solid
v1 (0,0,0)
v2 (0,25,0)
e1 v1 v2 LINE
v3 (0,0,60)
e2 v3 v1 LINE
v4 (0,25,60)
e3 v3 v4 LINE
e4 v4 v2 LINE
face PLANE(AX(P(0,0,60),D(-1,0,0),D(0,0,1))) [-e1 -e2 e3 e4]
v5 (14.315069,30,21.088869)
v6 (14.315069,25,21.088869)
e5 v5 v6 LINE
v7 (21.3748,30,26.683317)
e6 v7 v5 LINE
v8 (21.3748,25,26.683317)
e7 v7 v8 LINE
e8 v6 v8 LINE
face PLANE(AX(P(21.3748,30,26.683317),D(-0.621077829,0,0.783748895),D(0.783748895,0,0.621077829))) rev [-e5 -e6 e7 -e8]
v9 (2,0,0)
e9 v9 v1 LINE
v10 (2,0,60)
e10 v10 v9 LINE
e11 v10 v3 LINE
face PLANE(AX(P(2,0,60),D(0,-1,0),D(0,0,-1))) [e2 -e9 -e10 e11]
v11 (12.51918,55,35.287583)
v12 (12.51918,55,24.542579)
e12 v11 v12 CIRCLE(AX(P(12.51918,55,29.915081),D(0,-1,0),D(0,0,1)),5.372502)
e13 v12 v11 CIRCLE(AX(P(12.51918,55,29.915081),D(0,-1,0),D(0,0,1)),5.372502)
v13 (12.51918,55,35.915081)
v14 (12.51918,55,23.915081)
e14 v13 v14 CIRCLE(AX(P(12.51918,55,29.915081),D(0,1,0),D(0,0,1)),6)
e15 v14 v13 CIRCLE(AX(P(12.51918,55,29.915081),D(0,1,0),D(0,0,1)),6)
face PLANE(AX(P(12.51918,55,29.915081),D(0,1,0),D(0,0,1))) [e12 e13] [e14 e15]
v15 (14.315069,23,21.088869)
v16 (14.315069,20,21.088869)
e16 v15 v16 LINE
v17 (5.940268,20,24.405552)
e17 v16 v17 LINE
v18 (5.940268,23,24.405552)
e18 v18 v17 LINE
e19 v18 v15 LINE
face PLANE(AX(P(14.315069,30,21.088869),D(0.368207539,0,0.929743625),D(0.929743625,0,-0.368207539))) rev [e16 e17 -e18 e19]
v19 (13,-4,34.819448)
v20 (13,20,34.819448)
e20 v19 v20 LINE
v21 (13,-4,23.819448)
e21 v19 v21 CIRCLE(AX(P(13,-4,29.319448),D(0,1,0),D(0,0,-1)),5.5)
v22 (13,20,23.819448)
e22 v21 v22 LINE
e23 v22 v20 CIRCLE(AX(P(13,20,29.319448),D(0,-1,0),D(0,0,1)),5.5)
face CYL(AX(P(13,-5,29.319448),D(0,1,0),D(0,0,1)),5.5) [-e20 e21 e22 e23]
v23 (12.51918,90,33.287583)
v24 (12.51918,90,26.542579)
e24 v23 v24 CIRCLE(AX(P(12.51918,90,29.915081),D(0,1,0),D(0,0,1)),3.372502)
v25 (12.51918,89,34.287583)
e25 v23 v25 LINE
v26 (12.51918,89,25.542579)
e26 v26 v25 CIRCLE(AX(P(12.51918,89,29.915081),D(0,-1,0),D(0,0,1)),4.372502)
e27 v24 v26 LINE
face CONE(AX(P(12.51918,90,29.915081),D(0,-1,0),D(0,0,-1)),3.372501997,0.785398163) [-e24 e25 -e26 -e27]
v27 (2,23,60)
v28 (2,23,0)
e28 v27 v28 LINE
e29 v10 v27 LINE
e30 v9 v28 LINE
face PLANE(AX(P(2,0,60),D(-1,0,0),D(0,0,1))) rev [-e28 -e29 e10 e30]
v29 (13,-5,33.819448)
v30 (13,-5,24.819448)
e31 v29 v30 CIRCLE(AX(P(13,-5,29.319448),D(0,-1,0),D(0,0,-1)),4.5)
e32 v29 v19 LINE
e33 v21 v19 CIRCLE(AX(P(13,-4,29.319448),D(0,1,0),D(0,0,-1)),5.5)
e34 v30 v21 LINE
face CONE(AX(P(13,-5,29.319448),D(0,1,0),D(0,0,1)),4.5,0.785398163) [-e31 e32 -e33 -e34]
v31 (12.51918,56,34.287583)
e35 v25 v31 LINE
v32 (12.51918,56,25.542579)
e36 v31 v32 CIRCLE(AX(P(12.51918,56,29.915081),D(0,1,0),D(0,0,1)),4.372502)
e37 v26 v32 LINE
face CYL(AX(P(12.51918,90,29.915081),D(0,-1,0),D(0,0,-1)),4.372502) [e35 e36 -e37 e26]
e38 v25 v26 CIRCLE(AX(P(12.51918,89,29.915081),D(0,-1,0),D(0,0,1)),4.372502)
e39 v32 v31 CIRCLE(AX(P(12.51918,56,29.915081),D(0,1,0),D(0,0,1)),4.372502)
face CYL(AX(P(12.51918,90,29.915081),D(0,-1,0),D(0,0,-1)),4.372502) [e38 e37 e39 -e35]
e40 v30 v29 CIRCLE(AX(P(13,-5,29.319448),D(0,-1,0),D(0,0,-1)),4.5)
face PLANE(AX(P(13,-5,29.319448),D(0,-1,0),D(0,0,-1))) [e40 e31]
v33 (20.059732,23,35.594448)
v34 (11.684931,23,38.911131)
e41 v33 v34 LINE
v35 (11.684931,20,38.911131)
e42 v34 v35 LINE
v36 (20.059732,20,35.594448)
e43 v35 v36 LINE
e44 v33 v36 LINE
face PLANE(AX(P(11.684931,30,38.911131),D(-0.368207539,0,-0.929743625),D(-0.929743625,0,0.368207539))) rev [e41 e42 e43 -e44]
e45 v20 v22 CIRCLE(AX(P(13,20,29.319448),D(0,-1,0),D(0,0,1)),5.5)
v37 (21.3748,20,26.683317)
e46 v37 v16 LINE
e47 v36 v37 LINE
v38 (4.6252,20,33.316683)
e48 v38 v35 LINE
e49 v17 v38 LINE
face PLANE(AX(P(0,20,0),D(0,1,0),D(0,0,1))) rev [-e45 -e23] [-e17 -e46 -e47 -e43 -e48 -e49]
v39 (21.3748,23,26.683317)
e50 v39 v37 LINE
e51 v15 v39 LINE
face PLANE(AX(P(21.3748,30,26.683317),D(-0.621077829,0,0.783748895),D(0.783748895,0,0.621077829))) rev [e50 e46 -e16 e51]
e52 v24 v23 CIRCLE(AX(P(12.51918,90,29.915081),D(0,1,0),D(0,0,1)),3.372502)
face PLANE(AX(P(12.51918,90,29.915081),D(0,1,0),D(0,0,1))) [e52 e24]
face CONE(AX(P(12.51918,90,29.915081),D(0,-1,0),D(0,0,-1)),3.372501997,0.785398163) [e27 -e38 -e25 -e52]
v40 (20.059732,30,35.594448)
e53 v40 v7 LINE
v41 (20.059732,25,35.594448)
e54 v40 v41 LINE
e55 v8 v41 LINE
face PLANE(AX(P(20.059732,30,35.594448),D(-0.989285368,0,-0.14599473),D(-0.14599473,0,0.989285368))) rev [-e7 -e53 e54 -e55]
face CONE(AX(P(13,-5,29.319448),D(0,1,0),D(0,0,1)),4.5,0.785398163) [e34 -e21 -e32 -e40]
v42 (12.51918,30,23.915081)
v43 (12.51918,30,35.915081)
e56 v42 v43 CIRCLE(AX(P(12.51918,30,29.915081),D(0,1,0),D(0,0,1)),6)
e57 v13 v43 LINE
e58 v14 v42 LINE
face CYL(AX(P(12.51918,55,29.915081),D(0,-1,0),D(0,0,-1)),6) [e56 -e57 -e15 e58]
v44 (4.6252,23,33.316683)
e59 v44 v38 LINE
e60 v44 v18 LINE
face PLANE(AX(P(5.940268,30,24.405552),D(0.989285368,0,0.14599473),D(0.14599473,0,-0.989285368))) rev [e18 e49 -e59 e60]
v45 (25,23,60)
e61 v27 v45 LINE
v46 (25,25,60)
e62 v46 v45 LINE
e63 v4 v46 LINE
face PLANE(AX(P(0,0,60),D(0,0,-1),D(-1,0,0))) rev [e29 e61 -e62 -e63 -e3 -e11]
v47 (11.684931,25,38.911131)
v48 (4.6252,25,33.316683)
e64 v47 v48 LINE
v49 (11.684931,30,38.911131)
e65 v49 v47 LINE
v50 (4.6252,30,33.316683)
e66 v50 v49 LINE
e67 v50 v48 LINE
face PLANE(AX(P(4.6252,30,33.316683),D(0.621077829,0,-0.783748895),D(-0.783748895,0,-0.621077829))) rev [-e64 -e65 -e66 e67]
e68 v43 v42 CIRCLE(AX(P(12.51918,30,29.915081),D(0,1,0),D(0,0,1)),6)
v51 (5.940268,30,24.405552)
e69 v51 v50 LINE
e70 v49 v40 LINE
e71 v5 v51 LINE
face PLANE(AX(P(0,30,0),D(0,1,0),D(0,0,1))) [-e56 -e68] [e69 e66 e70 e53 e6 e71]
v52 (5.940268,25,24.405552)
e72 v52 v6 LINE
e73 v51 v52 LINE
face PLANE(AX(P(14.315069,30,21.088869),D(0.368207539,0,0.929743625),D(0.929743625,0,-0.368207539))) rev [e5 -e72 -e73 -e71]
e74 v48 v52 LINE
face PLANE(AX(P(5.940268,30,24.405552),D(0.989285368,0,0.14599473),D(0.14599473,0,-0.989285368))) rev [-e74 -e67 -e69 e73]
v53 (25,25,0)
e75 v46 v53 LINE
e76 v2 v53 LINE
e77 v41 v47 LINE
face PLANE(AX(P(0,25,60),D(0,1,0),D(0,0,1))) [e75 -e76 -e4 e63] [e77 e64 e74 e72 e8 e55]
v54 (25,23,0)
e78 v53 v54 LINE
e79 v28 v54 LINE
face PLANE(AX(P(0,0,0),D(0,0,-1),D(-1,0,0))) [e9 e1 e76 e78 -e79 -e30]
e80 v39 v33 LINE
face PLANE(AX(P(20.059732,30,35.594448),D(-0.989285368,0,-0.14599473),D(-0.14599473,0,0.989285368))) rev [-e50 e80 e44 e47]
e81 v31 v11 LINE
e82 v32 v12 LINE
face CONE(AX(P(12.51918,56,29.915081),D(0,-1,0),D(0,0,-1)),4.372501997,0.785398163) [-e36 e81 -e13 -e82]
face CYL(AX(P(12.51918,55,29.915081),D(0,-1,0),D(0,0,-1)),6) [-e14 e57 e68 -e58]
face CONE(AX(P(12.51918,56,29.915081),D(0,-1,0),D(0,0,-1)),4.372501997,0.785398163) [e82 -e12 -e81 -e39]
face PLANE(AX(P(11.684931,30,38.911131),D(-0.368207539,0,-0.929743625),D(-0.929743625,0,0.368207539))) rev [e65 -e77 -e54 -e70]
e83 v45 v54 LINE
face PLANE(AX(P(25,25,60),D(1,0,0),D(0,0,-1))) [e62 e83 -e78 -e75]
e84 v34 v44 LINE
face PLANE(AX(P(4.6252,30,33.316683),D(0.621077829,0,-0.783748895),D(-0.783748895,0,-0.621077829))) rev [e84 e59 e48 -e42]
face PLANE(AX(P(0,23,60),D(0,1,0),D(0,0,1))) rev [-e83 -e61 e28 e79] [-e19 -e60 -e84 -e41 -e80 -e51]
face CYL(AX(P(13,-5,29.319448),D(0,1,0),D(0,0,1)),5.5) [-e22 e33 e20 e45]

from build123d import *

# Parameters (mm, degrees)
EXTRUDE_THIN1_DEPTH = 60
BOSS_EXTRUDE2_DEPTH = 5
SKETCH4_R           = 5.5
BOSS_EXTRUDE3_DEPTH = 25
SKETCH5_R           = 6
BOSS_EXTRUDE4_DEPTH = 25
SKETCH6_R           = 4.372501997
BOSS_EXTRUDE5_DEPTH = 35
CHAMFER1_SIZE       = 1


with BuildPart() as part:
    # Sketch2 → Extrude-Thin1 (new body)
    with BuildSketch(Plane.XY):
        Polygon((0, 0), (0, 25), (25, 25), (25, 23), (2, 23), (2, 0), align=None)
    extrude(amount=EXTRUDE_THIN1_DEPTH)

    # Sketch3 → Boss-Extrude2 (add, symmetric)
    with BuildSketch(Plane(origin=(0, 25, 0), x_dir=(1, 0, 0), z_dir=(0, 1, 0))):
        Polygon((11.684931341, -38.911131142), (20.059731616, -35.594448438), (21.374800275, -26.683317296), (14.315068659, -21.088868858), (5.940268384, -24.405551562), (4.625199725, -33.316682704), align=None)
    extrude(amount=BOSS_EXTRUDE2_DEPTH, both=True)

    # Sketch4 → Boss-Extrude3 (add)
    with BuildSketch(Plane(origin=(0, 20, 0), x_dir=(-1, 0, 0), z_dir=(0, -1, 0))):
        with Locations(Location((-13, -29.319447598, 0), (0, 0, 270))):
            Circle(SKETCH4_R)
    extrude(amount=BOSS_EXTRUDE3_DEPTH)

    # Sketch5 → Boss-Extrude4 (add)
    with BuildSketch(Plane(origin=(0, 30, 0), x_dir=(1, 0, 0), z_dir=(0, 1, 0))):
        with Locations(Location((12.519179725, -29.915081058, 0), (0, 0, 270))):
            Circle(SKETCH5_R)
    extrude(amount=BOSS_EXTRUDE4_DEPTH)

    # Sketch6 → Boss-Extrude5 (add)
    with BuildSketch(Plane(origin=(0, 55, 0), x_dir=(1, 0, 0), z_dir=(0, 1, 0))):
        with Locations(Location((12.519179725, -29.915081058, 0), (0, 0, 270))):
            Circle(SKETCH6_R)
    extrude(amount=BOSS_EXTRUDE5_DEPTH)

    # Chamfer1
    chamfer1_edges = [part.edges().sort_by_distance(p)[0] for p in [
        (13, -5, 23.819447598),
        (12.519179725, 55, 25.542579061),
        (12.519179725, 90, 25.542579061),
    ]]
    chamfer(chamfer1_edges, length=CHAMFER1_SIZE)


solid = part.part
